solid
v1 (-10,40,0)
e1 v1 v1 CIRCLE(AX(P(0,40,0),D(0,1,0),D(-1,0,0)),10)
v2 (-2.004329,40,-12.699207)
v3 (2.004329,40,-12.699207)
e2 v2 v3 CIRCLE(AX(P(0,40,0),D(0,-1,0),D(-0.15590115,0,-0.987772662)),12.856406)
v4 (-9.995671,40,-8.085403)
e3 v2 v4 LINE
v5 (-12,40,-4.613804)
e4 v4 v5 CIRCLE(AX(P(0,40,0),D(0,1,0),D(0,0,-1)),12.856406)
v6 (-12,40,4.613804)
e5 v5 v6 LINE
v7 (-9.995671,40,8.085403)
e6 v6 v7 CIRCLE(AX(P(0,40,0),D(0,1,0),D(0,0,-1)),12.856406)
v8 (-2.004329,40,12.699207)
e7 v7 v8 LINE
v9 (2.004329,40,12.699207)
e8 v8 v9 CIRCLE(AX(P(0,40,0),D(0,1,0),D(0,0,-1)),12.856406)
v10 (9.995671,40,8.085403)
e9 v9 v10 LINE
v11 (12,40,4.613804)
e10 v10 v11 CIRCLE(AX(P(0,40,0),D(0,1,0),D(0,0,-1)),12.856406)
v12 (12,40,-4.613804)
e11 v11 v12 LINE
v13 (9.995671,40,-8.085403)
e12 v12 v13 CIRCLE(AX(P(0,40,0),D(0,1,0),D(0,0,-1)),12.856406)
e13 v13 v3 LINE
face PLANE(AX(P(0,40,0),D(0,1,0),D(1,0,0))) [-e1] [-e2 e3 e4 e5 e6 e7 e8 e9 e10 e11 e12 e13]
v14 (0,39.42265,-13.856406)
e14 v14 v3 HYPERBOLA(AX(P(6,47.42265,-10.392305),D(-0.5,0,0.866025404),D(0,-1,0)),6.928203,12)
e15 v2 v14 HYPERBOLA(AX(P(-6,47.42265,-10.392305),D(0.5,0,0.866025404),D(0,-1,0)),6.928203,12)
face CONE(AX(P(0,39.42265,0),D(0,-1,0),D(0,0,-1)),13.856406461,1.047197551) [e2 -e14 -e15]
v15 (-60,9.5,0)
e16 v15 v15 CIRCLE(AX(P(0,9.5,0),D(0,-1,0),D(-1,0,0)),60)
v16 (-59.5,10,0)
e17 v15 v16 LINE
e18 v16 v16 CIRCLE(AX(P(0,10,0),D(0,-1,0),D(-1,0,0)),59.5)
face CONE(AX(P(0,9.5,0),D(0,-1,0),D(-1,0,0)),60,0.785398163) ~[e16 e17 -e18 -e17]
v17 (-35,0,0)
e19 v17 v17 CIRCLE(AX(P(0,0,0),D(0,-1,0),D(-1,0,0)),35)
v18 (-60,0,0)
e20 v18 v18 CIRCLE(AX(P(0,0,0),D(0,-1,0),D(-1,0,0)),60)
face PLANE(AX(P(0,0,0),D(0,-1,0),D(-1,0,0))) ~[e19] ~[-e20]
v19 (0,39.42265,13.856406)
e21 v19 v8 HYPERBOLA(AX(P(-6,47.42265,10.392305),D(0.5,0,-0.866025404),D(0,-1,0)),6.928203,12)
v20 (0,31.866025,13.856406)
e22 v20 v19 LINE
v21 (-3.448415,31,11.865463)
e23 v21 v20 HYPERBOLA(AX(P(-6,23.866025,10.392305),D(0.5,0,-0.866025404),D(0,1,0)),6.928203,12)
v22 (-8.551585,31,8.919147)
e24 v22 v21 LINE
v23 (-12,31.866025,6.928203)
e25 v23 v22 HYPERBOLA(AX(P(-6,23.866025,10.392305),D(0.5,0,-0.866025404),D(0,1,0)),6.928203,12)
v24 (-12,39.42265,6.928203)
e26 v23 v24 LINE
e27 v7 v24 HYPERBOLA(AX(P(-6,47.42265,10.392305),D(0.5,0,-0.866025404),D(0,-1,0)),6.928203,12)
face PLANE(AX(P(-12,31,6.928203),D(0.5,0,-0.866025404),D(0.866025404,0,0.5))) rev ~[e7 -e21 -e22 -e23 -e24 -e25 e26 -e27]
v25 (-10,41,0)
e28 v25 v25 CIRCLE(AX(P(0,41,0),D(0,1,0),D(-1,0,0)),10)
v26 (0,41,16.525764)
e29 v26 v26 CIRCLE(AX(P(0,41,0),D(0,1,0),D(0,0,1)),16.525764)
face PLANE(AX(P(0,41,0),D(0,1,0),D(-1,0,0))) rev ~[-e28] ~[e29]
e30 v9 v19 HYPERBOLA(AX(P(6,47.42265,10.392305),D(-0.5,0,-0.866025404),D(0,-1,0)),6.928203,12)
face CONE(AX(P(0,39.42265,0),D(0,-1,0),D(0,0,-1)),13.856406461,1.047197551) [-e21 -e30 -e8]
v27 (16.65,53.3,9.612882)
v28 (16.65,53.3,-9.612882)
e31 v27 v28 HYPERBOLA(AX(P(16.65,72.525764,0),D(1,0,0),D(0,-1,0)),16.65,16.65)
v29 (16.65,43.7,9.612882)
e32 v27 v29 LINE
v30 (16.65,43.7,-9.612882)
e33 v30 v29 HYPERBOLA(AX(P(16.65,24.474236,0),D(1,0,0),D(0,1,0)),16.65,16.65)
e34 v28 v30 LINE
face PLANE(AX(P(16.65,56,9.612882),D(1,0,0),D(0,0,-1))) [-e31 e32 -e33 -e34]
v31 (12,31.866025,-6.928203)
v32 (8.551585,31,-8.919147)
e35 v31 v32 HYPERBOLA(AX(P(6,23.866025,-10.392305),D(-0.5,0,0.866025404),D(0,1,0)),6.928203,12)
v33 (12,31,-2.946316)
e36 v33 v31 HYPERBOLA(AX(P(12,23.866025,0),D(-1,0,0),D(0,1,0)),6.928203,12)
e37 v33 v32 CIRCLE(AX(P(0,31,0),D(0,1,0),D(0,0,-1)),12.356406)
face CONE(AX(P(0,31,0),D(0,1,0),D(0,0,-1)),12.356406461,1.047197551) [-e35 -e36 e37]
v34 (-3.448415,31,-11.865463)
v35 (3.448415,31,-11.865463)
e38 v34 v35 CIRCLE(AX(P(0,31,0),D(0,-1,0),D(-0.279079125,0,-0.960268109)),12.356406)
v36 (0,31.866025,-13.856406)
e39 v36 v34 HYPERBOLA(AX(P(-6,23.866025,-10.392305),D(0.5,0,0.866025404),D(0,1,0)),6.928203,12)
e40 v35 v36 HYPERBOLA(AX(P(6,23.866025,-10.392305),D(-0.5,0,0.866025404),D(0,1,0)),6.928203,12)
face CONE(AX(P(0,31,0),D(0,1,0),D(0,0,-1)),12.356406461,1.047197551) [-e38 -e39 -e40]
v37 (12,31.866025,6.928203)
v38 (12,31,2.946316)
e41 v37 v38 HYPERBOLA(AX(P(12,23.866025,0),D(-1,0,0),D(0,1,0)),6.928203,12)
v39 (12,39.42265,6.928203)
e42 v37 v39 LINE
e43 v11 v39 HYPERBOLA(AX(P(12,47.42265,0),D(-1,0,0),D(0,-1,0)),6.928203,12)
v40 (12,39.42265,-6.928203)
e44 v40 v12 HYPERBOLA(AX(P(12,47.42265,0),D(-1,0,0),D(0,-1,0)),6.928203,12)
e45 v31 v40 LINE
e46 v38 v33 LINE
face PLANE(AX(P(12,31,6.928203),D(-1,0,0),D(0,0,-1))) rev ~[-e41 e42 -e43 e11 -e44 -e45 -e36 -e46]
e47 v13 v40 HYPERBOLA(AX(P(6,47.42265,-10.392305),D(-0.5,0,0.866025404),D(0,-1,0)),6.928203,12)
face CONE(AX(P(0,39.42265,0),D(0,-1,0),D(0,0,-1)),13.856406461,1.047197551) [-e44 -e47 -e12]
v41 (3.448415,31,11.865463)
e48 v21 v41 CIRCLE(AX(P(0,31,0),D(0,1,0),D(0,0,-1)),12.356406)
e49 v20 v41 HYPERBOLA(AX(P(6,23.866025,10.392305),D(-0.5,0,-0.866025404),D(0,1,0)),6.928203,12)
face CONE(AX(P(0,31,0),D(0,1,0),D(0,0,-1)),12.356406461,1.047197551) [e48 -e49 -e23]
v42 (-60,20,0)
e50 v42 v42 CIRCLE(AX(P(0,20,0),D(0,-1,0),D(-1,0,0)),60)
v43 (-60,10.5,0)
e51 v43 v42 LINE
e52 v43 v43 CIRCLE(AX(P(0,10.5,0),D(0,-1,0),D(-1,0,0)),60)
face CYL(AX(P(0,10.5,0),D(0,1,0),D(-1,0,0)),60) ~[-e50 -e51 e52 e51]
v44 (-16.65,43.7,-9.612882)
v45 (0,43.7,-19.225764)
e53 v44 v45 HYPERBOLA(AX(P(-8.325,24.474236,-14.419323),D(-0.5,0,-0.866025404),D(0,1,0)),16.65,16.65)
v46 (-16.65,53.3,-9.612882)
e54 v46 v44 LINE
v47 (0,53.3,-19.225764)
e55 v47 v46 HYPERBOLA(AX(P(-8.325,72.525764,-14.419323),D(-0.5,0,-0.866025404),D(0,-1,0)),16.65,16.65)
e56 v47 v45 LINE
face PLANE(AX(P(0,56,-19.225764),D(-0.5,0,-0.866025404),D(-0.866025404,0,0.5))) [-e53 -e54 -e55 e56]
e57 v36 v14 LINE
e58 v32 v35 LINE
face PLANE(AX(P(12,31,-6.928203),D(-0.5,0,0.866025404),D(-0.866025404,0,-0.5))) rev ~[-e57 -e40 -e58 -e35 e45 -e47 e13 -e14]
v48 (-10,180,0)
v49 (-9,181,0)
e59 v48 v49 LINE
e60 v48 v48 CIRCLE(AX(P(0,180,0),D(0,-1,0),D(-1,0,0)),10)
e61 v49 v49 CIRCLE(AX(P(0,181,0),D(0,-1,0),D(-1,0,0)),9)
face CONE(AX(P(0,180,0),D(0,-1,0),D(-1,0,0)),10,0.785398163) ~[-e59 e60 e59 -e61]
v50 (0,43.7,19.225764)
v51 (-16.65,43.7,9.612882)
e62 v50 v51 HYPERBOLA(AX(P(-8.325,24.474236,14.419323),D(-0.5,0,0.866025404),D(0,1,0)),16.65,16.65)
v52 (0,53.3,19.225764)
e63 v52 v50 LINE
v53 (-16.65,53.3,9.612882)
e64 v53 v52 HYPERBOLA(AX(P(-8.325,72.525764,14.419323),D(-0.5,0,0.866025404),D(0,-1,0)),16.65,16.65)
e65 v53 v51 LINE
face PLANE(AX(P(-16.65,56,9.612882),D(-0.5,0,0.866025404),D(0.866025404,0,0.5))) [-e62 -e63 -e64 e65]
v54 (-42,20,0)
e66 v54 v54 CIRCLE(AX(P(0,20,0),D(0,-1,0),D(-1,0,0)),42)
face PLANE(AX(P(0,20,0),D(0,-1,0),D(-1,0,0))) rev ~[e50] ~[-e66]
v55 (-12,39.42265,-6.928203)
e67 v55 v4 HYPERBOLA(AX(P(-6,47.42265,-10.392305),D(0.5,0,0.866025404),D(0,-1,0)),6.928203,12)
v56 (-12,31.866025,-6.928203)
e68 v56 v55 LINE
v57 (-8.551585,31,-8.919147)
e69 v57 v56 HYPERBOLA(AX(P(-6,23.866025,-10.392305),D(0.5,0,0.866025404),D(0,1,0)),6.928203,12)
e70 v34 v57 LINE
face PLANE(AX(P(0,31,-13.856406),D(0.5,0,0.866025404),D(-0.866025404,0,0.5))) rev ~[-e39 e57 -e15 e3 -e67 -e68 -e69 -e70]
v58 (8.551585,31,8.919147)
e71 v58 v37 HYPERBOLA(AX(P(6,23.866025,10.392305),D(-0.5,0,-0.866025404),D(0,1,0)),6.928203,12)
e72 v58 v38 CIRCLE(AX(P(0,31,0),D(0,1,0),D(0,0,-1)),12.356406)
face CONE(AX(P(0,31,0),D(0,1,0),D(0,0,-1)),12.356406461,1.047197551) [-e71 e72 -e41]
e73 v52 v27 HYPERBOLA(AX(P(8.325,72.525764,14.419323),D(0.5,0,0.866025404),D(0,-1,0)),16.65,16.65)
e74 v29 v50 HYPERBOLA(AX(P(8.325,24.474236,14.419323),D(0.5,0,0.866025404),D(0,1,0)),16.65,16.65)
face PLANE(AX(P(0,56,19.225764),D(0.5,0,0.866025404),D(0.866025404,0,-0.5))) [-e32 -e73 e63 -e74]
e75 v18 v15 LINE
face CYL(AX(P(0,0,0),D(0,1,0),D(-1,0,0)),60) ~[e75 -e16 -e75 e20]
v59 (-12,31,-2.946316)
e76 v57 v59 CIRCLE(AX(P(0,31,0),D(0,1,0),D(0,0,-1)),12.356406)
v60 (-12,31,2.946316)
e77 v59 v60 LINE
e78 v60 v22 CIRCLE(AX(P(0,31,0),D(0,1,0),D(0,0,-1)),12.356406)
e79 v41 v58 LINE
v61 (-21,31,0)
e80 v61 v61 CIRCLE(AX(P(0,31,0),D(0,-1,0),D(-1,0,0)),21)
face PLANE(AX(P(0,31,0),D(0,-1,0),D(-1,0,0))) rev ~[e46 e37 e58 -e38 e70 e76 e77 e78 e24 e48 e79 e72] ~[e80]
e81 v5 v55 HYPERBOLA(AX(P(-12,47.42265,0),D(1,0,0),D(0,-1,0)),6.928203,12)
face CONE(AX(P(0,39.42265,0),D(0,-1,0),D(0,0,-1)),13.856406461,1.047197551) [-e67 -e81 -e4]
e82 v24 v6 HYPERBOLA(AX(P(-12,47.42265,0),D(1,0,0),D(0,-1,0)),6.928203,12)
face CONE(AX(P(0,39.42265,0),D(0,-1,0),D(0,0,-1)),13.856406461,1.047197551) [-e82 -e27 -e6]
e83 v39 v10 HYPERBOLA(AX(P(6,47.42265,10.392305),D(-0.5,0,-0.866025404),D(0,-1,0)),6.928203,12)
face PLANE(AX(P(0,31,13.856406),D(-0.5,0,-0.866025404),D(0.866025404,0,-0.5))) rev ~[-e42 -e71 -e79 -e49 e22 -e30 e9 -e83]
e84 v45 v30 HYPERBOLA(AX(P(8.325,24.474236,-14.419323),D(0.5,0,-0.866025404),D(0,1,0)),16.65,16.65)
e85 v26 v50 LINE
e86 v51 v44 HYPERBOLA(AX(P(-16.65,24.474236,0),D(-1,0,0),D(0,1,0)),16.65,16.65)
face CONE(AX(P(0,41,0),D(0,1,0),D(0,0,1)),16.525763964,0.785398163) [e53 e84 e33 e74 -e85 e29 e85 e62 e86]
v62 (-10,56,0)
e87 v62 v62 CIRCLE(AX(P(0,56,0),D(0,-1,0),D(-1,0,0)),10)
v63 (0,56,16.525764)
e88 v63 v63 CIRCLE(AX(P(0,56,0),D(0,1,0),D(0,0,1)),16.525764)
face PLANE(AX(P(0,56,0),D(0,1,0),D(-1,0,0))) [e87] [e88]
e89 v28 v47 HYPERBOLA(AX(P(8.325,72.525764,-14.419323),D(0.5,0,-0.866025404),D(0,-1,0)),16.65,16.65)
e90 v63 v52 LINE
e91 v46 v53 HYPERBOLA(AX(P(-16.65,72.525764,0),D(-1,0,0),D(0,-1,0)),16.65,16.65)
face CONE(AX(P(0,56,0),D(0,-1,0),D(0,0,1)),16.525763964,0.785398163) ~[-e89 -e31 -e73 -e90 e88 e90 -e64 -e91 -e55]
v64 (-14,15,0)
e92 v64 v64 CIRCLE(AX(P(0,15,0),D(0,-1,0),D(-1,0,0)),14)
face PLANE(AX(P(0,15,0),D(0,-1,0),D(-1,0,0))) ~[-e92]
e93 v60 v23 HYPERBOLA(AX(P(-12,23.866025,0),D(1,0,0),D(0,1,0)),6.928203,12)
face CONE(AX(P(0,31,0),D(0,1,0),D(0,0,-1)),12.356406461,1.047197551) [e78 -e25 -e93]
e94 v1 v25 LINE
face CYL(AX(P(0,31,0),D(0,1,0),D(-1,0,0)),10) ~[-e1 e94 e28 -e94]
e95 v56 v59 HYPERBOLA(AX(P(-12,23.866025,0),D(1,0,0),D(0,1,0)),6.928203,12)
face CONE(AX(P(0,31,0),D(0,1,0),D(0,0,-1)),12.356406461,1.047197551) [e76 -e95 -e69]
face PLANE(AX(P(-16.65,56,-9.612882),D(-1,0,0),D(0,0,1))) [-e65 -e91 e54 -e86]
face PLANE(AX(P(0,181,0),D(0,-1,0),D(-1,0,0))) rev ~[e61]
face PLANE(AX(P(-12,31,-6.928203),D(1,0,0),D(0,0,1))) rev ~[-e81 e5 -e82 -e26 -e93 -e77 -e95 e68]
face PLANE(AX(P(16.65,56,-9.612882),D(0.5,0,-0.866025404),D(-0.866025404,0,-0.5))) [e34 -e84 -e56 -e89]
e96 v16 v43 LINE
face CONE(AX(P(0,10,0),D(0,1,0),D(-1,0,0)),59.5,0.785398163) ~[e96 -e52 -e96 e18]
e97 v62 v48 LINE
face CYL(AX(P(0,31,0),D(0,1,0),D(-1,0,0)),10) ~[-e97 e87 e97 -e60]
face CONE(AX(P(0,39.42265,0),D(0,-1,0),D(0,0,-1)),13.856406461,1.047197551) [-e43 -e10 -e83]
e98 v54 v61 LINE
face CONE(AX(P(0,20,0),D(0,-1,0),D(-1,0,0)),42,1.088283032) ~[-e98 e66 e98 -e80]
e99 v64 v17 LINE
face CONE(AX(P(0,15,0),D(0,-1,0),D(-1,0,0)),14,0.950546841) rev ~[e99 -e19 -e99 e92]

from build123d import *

# Parameters (mm, degrees)
BOSS_EXTRUDE1_DEPTH = 9
BOSS_EXTRUDE2_START = 15
SKETCH5_R           = 10
BOSS_EXTRUDE2_DEPTH = 15
CHAMFER1_SIZE       = 1


with BuildPart() as part:
    # Sketch1 → Revolve1 (revolve)
    with BuildSketch(Plane.XY, mode=Mode.PRIVATE) as revolve1_sk:
        Polygon((35, 0), (60, 0), (60, 9.5), (59.5, 10), (60, 10.5), (60, 20), (42, 20), (21, 31), (10, 31), (10, 181), (0, 181), (0, 15), (14, 15), align=None)
    revolve(revolve1_sk.sketch.rotate(Axis((0, 181, 0), (0, -1, 0)), 180), axis=Axis((0, 181, 0), (0, -1, 0)))

    # Sketch2 → Boss-Extrude1 (add)
    with BuildSketch(Plane(origin=(0, 31, 0), x_dir=(1, 0, 0), z_dir=(0, 1, 0))):
        Polygon((12, 6.92820323), (0, 13.856406461), (-12, 6.92820323), (-12, -6.92820323), (0, -13.856406461), (12, -6.92820323), align=None)
    extrude(amount=BOSS_EXTRUDE1_DEPTH)

    # Sketch3 → Cut-Revolve1 (revolve, cut)
    with BuildSketch(Plane(origin=(0, 0, 0), x_dir=(0, 0, -1), z_dir=(1, 0, 0))):
        Polygon((12.356406461, 31), (13.856406461, 31.866025404), (13.856406461, 31), align=None)
        Polygon((13.856406461, 39.422649731), (12.856406461, 40), (13.856406461, 40), align=None)
    revolve(axis=Axis((0, 181, 0), (0, 1, 0)), mode=Mode.SUBTRACT)

    # Sketch5 → Boss-Extrude2 (add)
    with BuildSketch(Plane(origin=(0, 41, 0), x_dir=(-1, 0, 0), z_dir=(0, 1, 0)).offset(BOSS_EXTRUDE2_START)):
        Polygon((0, 19.225763964), (-16.65, 9.612881982), (-16.65, -9.612881982), (0, -19.225763964), (16.65, -9.612881982), (16.65, 9.612881982), align=None)
        with Locations(Location((0, 0, 0), (0, 0, 90))):
            Circle(SKETCH5_R, mode=Mode.SUBTRACT)
    extrude(amount=-BOSS_EXTRUDE2_DEPTH)

    # Sketch7 → Cut-Revolve3 (revolve, cut)
    with BuildSketch(Plane(origin=(0, 0, 0), x_dir=(0, 0, -1), z_dir=(1, 0, 0)), mode=Mode.PRIVATE) as cut_revolve3_sk:
        Polygon((16.525763964, 56), (19.225763964, 53.3), (19.225763964, 56), align=None)
        Polygon((16.525763964, 41), (19.225763964, 43.7), (19.225763964, 41), align=None)
    revolve(cut_revolve3_sk.sketch.rotate(Axis((0, 181, 0), (0, 1, 0)), 180), axis=Axis((0, 181, 0), (0, 1, 0)), mode=Mode.SUBTRACT)

    # Chamfer1
    chamfer1_edges = [part.edges().sort_by_distance(p)[0] for p in [
        (10, 181, 0),
    ]]
    chamfer(chamfer1_edges, length=CHAMFER1_SIZE)


solid = part.part
